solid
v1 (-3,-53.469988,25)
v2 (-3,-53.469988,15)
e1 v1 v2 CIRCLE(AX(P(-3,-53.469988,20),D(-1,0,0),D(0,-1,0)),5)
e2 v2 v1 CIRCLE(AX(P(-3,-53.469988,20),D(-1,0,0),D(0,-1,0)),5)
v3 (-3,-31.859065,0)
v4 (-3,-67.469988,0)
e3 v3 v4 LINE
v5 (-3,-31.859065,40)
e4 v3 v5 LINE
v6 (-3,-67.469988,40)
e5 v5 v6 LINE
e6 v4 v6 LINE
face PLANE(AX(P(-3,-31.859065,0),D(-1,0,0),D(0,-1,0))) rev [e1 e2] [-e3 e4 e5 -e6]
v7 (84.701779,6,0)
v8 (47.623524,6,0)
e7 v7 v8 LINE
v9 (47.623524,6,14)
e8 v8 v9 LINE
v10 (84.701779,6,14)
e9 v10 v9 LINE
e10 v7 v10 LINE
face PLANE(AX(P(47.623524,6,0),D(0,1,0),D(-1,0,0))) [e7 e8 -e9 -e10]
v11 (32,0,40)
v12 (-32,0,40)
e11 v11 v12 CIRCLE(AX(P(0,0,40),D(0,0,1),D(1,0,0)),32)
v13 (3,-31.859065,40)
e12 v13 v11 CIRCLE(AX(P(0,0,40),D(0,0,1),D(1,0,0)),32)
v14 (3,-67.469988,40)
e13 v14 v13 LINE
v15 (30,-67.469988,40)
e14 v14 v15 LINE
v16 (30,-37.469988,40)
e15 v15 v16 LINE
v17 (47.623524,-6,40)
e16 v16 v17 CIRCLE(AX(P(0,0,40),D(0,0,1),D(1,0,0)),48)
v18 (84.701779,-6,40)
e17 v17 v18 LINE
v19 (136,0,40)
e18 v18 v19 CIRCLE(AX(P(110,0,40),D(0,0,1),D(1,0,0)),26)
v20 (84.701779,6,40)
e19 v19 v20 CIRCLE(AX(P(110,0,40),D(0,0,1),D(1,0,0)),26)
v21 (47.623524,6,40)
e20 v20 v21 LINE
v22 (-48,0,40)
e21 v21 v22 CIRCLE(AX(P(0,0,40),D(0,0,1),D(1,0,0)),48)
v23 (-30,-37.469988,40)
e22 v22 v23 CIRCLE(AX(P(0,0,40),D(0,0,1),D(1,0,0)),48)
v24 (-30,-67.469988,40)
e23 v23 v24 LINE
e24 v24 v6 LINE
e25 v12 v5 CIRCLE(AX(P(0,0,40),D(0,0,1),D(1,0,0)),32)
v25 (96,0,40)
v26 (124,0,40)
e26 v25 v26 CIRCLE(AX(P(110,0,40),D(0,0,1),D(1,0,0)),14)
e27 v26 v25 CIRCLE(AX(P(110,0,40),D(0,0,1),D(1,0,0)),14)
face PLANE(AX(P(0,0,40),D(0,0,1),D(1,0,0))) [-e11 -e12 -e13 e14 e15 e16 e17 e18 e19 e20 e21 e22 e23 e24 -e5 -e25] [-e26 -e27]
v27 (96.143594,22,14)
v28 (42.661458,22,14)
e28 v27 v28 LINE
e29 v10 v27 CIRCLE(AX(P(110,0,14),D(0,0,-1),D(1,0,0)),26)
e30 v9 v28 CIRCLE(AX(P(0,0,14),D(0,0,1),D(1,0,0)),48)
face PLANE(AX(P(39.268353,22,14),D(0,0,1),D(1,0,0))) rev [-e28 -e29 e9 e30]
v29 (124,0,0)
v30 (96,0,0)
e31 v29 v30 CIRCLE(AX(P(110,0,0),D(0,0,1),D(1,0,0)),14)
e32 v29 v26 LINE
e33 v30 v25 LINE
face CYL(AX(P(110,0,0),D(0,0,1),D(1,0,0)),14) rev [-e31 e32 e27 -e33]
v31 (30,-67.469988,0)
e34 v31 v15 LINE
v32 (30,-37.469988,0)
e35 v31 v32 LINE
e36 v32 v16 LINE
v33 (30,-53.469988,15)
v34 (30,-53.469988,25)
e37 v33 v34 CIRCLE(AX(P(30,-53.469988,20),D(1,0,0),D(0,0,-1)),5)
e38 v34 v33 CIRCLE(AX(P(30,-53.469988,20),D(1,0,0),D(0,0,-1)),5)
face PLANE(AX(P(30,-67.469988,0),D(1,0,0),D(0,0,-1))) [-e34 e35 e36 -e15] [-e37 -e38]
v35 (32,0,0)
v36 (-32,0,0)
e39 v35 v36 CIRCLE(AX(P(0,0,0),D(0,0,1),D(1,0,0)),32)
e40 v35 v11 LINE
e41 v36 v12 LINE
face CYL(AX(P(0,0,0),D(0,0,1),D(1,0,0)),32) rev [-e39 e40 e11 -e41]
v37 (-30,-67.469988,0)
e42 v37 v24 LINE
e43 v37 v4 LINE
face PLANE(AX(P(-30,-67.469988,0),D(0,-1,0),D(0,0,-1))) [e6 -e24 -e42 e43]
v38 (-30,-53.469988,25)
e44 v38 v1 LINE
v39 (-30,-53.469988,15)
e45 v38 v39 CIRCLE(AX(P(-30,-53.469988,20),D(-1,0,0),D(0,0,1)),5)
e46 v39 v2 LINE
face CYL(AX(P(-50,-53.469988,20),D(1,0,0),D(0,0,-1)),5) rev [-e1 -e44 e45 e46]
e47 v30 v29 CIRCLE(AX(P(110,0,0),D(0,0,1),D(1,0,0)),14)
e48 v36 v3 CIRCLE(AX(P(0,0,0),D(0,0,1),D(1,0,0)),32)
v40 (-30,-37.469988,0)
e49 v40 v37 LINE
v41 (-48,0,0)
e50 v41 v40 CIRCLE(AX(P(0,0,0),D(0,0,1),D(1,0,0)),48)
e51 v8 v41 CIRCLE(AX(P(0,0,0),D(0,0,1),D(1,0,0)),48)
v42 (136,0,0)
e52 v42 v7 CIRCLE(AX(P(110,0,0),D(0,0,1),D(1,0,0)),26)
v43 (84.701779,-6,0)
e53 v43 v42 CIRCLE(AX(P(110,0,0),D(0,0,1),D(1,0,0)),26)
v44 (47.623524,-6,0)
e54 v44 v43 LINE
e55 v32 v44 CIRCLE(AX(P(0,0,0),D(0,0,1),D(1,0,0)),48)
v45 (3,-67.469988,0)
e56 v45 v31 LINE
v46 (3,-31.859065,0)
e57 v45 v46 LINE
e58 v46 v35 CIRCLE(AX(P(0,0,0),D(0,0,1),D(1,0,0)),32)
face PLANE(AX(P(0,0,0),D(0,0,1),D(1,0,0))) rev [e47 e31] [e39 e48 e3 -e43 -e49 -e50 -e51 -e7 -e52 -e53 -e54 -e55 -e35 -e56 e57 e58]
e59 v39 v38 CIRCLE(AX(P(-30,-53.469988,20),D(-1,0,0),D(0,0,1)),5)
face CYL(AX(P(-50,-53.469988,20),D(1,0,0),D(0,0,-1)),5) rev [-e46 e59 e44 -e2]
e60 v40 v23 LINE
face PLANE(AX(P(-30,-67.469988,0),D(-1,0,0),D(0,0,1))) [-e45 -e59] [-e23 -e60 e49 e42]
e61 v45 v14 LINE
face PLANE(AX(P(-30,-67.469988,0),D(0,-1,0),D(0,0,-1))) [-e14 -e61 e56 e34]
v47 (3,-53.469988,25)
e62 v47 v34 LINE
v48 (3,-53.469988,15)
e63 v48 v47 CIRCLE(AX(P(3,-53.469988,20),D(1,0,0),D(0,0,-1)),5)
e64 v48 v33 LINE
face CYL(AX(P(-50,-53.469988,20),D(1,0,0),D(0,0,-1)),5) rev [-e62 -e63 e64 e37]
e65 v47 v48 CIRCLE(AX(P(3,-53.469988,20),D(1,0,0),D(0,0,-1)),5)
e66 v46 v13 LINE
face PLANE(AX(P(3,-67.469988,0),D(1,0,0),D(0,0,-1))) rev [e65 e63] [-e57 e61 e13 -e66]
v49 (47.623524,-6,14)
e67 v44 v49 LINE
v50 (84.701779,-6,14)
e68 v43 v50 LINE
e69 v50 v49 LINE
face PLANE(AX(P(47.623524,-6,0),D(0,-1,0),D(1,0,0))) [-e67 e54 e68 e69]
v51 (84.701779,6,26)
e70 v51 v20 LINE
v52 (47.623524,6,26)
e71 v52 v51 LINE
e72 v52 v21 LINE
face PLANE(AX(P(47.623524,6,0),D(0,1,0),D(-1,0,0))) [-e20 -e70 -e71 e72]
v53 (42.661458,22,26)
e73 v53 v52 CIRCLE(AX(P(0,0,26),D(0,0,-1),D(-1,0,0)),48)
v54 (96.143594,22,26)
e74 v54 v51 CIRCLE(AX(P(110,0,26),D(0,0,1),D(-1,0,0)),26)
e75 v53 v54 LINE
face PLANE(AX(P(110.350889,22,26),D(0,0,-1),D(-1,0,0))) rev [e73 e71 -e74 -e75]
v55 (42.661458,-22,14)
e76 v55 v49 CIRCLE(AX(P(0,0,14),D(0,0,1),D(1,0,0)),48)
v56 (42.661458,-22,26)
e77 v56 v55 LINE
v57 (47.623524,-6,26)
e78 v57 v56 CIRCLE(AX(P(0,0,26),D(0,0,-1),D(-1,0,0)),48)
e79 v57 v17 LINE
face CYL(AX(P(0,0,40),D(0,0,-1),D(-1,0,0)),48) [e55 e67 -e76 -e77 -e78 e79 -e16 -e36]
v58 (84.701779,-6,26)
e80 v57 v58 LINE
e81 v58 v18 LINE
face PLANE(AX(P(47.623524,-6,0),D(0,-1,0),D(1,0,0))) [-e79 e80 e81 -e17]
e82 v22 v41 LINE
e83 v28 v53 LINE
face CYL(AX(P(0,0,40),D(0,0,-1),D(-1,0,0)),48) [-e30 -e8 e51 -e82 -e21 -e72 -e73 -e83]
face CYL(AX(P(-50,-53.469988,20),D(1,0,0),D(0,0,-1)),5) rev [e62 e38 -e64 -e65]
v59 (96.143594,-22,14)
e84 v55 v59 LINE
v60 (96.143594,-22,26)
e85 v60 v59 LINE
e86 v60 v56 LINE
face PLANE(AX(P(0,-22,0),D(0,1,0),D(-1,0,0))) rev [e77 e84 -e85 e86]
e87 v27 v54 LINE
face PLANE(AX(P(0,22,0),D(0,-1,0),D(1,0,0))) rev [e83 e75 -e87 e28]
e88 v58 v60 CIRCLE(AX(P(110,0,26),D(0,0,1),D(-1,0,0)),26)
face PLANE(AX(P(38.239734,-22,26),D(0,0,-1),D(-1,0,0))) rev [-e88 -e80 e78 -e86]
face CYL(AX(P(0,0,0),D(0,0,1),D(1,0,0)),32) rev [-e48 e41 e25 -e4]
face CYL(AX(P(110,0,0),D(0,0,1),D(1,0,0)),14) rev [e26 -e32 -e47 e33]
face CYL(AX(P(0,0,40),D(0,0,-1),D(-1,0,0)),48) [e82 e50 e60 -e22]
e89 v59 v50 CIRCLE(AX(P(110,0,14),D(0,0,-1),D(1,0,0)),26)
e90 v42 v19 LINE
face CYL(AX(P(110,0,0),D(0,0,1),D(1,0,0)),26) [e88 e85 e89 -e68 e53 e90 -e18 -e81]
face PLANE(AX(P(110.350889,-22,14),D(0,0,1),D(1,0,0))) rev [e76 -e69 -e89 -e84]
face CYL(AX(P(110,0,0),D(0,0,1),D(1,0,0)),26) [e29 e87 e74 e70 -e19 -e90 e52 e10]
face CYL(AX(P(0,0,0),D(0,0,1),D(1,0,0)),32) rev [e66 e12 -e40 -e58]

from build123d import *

# Parameters (mm, degrees)
CLAMP_RING_SKETCH_R             = 48
CLAMP_RING_96_DEPTH             = 40
CLAMP_START                     = -40
CLAMP_LUG_DEPTH                 = 40
CLAMP_BORE_AND_SPLIT_SLOT_DEPTH = 40
PIVOT_EYE_SKETCH_R              = 26
PIVOT_EYE_52_DEPTH              = 40
CONNECTING_START                = -40
CONNECTING_ARM_DEPTH            = 40
ARM_RIB_A_DEPTH                 = 16
ARM_RIB_B_DEPTH                 = 16
PIVOT_BORE_SKETCH_R             = 14
PIVOT_BORE_28_DEPTH             = 40
CLAMP_SCREW_HOLE_SKETCH_R       = 5
CLAMP_SCREW_HOLE_10_DEPTH       = 80


with BuildPart() as part:
    # Clamp Ring Sketch → Clamp Ring Ø96 (new body)
    with BuildSketch(Plane.XY):
        Circle(CLAMP_RING_SKETCH_R)
    extrude(amount=CLAMP_RING_96_DEPTH)

    # Clamp Lug Sketch → Clamp Lug (add)
    with BuildSketch(Plane.XY.offset(40).offset(CLAMP_START)):
        with BuildLine():
            Line((30, -67.46998799), (30, -37.46998799))
            ThreePointArc((30, -37.46998799), (0, -48), (-30, -37.46998799))
            Line((-30, -37.46998799), (-30, -67.46998799))
            Line((-30, -67.46998799), (30, -67.46998799))
        make_face()
    extrude(amount=CLAMP_LUG_DEPTH)

    # Clamp Bore and Split Sketch → Clamp Bore and Split Slot (cut)
    with BuildSketch(Plane.XY.offset(40)):
        with BuildLine():
            Line((-3, -67.46998799), (3, -67.46998799))
            Line((3, -67.46998799), (3, -31.859064644))
            ThreePointArc((3, -31.859064644), (0, 32), (-3, -31.859064644))
            Line((-3, -31.859064644), (-3, -67.46998799))
        make_face()
    extrude(amount=-CLAMP_BORE_AND_SPLIT_SLOT_DEPTH, mode=Mode.SUBTRACT)



with BuildPart() as body_2:
    # Pivot Eye Sketch → Pivot Eye Ø52 (new body)
    with BuildSketch(Plane.XY.offset(40)):
        with Locations((110, 0)):
            Circle(PIVOT_EYE_SKETCH_R)
    extrude(amount=-PIVOT_EYE_52_DEPTH)


with BuildPart() as part_1:
    add(part.part)

    add(body_2.part)  # Connecting Arm merges body 2
    # Connecting Arm Sketch → Connecting Arm (add)
    with BuildSketch(Plane.XY.offset(40).offset(CONNECTING_START)):
        with BuildLine():
            Line((47.623523599, 6), (84.701778719, 6))
            ThreePointArc((84.701778719, 6), (84, 0), (84.701778719, -6))
            Line((84.701778719, -6), (47.623523599, -6))
            ThreePointArc((47.623523599, -6), (48, 0), (47.623523599, 6))
        make_face()
    extrude(amount=CONNECTING_ARM_DEPTH)

    # Arm Rib A Sketch → Arm Rib A (add)
    with BuildSketch(Plane(origin=(0, 6, 0), x_dir=(1, 0, 0), z_dir=(0, 1, 0))):
        Polygon((98.516804154, -14), (110.350889359, -14), (110.350889359, -26), (98.516804154, -26), (39.268352847, -26), (39.268352847, -20), (39.268352847, -14), align=None)
    extrude(amount=ARM_RIB_A_DEPTH)

    # Arm Rib B Sketch → Arm Rib B (add)
    with BuildSketch(Plane.XZ.offset(6)):
        Polygon((38.239733901, 20), (38.239733901, 26), (110.350889359, 26), (110.350889359, 14), (38.239733901, 14), align=None)
    extrude(amount=ARM_RIB_B_DEPTH)

    # Pivot Bore Sketch → Pivot Bore Ø28 (cut)
    with BuildSketch(Plane.XY.offset(40)):
        with Locations((110, 0)):
            Circle(PIVOT_BORE_SKETCH_R)
    extrude(amount=-PIVOT_BORE_28_DEPTH, mode=Mode.SUBTRACT)

    # Clamp Screw Hole Sketch → Clamp Screw Hole Ø10 (cut)
    with BuildSketch(Plane(origin=(30, 0, 0), x_dir=(0, 0, -1), z_dir=(1, 0, 0))):
        with Locations(Location((-20, -53.46998799, 0), (0, 0, 270))):
            Circle(CLAMP_SCREW_HOLE_SKETCH_R)
    extrude(amount=-CLAMP_SCREW_HOLE_10_DEPTH, mode=Mode.SUBTRACT)


solid = part_1.part
